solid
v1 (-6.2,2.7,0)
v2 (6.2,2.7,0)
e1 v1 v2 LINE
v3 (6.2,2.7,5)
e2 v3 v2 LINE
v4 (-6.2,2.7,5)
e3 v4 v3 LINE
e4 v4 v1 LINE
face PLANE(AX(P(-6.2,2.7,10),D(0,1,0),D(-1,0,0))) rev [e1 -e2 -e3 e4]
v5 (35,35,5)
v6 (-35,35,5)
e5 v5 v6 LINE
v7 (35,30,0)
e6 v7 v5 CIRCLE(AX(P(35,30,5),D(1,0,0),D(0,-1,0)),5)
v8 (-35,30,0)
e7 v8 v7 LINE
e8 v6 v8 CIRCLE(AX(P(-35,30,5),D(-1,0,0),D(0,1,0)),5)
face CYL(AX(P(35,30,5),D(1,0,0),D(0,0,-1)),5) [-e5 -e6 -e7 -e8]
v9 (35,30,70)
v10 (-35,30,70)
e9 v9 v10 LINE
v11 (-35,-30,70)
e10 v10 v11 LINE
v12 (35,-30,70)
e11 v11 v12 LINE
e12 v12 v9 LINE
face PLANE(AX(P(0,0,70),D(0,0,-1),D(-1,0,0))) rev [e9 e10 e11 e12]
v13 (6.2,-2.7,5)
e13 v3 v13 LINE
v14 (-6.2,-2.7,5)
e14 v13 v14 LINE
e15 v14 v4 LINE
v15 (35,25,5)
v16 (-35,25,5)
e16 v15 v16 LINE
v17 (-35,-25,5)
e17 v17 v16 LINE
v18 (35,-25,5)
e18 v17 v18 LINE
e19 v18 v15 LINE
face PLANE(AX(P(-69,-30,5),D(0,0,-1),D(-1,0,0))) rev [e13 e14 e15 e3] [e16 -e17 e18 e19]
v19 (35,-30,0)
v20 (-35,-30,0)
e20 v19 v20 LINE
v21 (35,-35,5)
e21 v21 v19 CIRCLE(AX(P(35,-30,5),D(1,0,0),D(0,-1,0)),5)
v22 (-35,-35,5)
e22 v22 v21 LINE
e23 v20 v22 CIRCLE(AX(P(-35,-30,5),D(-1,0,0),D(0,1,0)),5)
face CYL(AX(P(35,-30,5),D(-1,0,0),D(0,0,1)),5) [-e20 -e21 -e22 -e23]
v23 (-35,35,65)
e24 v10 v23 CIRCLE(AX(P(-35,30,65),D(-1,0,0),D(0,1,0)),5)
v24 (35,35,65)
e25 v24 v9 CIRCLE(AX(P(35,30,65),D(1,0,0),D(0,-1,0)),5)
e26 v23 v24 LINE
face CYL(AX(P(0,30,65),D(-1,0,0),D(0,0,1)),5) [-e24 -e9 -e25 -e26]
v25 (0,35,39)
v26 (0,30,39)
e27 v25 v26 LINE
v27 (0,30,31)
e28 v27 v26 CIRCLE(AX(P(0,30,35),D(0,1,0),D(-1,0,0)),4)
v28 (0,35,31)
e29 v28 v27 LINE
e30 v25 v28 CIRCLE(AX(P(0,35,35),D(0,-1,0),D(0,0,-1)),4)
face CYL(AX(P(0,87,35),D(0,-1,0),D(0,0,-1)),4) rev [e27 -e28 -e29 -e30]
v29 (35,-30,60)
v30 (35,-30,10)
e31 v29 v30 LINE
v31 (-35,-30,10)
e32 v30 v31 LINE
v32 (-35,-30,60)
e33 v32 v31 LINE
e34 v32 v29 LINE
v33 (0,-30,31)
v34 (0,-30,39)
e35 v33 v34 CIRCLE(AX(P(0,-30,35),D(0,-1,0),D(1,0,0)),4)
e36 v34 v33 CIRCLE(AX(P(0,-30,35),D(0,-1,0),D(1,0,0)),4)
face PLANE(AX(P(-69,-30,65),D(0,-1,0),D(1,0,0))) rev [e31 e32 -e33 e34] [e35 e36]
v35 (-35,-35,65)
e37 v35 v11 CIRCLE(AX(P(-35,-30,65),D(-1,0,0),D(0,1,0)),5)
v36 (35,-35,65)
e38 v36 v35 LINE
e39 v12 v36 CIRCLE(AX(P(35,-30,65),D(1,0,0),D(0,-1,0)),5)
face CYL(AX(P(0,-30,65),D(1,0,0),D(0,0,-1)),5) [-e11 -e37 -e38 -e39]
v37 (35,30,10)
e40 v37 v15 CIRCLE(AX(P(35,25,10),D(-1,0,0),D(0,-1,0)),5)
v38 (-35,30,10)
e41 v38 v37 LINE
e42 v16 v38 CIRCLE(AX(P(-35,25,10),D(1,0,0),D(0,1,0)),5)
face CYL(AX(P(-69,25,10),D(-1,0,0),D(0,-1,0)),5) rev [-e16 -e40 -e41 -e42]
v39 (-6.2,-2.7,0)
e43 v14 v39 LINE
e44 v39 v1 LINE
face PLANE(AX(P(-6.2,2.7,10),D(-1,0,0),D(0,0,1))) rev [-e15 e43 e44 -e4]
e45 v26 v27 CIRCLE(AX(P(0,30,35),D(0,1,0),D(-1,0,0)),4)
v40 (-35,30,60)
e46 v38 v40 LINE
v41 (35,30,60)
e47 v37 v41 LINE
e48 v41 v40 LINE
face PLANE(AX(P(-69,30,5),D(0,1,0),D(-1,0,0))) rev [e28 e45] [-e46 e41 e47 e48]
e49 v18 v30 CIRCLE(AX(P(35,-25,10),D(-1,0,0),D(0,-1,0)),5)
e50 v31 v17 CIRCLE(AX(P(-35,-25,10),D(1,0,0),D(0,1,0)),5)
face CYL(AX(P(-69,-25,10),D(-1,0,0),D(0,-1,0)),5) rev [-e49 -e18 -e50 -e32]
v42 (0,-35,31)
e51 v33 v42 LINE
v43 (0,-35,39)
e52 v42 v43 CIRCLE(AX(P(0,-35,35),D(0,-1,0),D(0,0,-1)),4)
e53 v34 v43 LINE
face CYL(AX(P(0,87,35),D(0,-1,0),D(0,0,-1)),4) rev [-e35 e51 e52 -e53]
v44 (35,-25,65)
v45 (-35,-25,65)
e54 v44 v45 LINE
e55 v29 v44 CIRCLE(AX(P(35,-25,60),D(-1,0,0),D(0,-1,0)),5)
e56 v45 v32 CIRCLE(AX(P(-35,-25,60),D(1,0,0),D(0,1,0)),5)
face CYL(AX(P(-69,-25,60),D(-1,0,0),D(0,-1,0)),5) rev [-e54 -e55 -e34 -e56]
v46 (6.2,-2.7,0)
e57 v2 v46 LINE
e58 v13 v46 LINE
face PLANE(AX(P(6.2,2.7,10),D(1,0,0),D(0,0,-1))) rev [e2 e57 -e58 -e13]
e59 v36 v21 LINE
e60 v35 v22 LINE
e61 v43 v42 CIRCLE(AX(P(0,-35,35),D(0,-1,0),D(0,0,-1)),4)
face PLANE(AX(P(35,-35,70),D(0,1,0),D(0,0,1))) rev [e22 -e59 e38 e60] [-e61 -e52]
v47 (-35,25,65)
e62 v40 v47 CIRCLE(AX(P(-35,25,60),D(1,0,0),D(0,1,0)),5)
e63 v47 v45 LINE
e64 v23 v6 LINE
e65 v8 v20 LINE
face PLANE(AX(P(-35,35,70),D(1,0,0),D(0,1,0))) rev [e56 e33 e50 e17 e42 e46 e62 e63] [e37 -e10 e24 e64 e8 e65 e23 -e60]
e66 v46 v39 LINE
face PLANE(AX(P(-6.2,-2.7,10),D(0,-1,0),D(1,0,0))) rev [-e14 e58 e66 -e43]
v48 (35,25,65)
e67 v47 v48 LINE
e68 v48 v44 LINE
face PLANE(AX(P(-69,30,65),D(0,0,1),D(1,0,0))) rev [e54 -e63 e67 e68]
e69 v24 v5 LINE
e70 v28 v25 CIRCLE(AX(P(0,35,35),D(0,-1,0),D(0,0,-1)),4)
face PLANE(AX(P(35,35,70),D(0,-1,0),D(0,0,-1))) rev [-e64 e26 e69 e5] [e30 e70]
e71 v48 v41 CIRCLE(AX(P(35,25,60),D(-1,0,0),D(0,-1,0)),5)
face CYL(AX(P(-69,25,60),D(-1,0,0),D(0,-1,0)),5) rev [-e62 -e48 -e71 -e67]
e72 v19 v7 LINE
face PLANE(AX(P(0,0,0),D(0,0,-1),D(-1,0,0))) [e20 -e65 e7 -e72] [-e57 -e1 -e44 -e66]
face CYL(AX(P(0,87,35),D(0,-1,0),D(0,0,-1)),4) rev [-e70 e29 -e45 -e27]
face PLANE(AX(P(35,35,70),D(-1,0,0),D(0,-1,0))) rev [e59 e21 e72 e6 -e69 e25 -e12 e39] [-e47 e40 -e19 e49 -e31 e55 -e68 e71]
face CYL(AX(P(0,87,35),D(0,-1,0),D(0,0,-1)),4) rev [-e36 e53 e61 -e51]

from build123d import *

# Parameters (mm, degrees)
SKETCH1_W           = 70
SKETCH1_H           = 70
BOSS_EXTRUDE1_DEPTH = 70
SKETCH2_W           = 60
SKETCH2_H           = 60
CUT_EXTRUDE1_DEPTH  = 104
SKETCH3_W           = 12.4
SKETCH3_H           = 5.4
CUT_EXTRUDE2_DEPTH  = 10
SKETCH4_R           = 4
CUT_EXTRUDE3_DEPTH  = 122
FILLET1_R           = 5


with BuildPart() as part:
    # Sketch1 → Boss-Extrude1 (new body)
    with BuildSketch(Plane.XY):
        Rectangle(SKETCH1_W, SKETCH1_H)
    extrude(amount=BOSS_EXTRUDE1_DEPTH)

    # Sketch2 → Cut-Extrude1 (cut)
    with BuildSketch(Plane(origin=(35, 0, 0), x_dir=(0, 0, -1), z_dir=(1, 0, 0))):
        with Locations((-35, 0)):
            Rectangle(SKETCH2_W, SKETCH2_H)
    extrude(amount=-CUT_EXTRUDE1_DEPTH, mode=Mode.SUBTRACT)

    # Sketch3 → Cut-Extrude2 (cut)
    with BuildSketch(Plane(origin=(0, 0, 0), x_dir=(-1, 0, 0), z_dir=(0, 0, -1))):
        Rectangle(SKETCH3_W, SKETCH3_H)
    extrude(amount=-CUT_EXTRUDE2_DEPTH, mode=Mode.SUBTRACT)

    # Sketch4 → Cut-Extrude3 (cut)
    with BuildSketch(Plane.XZ.offset(35)):
        with Locations(Location((0, 35, 0), (0, 0, 270))):
            Circle(SKETCH4_R)
    extrude(amount=-CUT_EXTRUDE3_DEPTH, mode=Mode.SUBTRACT)

    # Fillet1
    fillet1_edges = [part.edges().sort_by_distance(p)[0] for p in [
        (0, 35, 70),
        (0, -30, 5),
        (0, -30, 65),
        (0, 30, 65),
        (0, 30, 5),
        (0, 35, 0),
        (0, -35, 0),
        (0, -35, 70),
    ]]
    fillet(fillet1_edges, radius=FILLET1_R)


solid = part.part
